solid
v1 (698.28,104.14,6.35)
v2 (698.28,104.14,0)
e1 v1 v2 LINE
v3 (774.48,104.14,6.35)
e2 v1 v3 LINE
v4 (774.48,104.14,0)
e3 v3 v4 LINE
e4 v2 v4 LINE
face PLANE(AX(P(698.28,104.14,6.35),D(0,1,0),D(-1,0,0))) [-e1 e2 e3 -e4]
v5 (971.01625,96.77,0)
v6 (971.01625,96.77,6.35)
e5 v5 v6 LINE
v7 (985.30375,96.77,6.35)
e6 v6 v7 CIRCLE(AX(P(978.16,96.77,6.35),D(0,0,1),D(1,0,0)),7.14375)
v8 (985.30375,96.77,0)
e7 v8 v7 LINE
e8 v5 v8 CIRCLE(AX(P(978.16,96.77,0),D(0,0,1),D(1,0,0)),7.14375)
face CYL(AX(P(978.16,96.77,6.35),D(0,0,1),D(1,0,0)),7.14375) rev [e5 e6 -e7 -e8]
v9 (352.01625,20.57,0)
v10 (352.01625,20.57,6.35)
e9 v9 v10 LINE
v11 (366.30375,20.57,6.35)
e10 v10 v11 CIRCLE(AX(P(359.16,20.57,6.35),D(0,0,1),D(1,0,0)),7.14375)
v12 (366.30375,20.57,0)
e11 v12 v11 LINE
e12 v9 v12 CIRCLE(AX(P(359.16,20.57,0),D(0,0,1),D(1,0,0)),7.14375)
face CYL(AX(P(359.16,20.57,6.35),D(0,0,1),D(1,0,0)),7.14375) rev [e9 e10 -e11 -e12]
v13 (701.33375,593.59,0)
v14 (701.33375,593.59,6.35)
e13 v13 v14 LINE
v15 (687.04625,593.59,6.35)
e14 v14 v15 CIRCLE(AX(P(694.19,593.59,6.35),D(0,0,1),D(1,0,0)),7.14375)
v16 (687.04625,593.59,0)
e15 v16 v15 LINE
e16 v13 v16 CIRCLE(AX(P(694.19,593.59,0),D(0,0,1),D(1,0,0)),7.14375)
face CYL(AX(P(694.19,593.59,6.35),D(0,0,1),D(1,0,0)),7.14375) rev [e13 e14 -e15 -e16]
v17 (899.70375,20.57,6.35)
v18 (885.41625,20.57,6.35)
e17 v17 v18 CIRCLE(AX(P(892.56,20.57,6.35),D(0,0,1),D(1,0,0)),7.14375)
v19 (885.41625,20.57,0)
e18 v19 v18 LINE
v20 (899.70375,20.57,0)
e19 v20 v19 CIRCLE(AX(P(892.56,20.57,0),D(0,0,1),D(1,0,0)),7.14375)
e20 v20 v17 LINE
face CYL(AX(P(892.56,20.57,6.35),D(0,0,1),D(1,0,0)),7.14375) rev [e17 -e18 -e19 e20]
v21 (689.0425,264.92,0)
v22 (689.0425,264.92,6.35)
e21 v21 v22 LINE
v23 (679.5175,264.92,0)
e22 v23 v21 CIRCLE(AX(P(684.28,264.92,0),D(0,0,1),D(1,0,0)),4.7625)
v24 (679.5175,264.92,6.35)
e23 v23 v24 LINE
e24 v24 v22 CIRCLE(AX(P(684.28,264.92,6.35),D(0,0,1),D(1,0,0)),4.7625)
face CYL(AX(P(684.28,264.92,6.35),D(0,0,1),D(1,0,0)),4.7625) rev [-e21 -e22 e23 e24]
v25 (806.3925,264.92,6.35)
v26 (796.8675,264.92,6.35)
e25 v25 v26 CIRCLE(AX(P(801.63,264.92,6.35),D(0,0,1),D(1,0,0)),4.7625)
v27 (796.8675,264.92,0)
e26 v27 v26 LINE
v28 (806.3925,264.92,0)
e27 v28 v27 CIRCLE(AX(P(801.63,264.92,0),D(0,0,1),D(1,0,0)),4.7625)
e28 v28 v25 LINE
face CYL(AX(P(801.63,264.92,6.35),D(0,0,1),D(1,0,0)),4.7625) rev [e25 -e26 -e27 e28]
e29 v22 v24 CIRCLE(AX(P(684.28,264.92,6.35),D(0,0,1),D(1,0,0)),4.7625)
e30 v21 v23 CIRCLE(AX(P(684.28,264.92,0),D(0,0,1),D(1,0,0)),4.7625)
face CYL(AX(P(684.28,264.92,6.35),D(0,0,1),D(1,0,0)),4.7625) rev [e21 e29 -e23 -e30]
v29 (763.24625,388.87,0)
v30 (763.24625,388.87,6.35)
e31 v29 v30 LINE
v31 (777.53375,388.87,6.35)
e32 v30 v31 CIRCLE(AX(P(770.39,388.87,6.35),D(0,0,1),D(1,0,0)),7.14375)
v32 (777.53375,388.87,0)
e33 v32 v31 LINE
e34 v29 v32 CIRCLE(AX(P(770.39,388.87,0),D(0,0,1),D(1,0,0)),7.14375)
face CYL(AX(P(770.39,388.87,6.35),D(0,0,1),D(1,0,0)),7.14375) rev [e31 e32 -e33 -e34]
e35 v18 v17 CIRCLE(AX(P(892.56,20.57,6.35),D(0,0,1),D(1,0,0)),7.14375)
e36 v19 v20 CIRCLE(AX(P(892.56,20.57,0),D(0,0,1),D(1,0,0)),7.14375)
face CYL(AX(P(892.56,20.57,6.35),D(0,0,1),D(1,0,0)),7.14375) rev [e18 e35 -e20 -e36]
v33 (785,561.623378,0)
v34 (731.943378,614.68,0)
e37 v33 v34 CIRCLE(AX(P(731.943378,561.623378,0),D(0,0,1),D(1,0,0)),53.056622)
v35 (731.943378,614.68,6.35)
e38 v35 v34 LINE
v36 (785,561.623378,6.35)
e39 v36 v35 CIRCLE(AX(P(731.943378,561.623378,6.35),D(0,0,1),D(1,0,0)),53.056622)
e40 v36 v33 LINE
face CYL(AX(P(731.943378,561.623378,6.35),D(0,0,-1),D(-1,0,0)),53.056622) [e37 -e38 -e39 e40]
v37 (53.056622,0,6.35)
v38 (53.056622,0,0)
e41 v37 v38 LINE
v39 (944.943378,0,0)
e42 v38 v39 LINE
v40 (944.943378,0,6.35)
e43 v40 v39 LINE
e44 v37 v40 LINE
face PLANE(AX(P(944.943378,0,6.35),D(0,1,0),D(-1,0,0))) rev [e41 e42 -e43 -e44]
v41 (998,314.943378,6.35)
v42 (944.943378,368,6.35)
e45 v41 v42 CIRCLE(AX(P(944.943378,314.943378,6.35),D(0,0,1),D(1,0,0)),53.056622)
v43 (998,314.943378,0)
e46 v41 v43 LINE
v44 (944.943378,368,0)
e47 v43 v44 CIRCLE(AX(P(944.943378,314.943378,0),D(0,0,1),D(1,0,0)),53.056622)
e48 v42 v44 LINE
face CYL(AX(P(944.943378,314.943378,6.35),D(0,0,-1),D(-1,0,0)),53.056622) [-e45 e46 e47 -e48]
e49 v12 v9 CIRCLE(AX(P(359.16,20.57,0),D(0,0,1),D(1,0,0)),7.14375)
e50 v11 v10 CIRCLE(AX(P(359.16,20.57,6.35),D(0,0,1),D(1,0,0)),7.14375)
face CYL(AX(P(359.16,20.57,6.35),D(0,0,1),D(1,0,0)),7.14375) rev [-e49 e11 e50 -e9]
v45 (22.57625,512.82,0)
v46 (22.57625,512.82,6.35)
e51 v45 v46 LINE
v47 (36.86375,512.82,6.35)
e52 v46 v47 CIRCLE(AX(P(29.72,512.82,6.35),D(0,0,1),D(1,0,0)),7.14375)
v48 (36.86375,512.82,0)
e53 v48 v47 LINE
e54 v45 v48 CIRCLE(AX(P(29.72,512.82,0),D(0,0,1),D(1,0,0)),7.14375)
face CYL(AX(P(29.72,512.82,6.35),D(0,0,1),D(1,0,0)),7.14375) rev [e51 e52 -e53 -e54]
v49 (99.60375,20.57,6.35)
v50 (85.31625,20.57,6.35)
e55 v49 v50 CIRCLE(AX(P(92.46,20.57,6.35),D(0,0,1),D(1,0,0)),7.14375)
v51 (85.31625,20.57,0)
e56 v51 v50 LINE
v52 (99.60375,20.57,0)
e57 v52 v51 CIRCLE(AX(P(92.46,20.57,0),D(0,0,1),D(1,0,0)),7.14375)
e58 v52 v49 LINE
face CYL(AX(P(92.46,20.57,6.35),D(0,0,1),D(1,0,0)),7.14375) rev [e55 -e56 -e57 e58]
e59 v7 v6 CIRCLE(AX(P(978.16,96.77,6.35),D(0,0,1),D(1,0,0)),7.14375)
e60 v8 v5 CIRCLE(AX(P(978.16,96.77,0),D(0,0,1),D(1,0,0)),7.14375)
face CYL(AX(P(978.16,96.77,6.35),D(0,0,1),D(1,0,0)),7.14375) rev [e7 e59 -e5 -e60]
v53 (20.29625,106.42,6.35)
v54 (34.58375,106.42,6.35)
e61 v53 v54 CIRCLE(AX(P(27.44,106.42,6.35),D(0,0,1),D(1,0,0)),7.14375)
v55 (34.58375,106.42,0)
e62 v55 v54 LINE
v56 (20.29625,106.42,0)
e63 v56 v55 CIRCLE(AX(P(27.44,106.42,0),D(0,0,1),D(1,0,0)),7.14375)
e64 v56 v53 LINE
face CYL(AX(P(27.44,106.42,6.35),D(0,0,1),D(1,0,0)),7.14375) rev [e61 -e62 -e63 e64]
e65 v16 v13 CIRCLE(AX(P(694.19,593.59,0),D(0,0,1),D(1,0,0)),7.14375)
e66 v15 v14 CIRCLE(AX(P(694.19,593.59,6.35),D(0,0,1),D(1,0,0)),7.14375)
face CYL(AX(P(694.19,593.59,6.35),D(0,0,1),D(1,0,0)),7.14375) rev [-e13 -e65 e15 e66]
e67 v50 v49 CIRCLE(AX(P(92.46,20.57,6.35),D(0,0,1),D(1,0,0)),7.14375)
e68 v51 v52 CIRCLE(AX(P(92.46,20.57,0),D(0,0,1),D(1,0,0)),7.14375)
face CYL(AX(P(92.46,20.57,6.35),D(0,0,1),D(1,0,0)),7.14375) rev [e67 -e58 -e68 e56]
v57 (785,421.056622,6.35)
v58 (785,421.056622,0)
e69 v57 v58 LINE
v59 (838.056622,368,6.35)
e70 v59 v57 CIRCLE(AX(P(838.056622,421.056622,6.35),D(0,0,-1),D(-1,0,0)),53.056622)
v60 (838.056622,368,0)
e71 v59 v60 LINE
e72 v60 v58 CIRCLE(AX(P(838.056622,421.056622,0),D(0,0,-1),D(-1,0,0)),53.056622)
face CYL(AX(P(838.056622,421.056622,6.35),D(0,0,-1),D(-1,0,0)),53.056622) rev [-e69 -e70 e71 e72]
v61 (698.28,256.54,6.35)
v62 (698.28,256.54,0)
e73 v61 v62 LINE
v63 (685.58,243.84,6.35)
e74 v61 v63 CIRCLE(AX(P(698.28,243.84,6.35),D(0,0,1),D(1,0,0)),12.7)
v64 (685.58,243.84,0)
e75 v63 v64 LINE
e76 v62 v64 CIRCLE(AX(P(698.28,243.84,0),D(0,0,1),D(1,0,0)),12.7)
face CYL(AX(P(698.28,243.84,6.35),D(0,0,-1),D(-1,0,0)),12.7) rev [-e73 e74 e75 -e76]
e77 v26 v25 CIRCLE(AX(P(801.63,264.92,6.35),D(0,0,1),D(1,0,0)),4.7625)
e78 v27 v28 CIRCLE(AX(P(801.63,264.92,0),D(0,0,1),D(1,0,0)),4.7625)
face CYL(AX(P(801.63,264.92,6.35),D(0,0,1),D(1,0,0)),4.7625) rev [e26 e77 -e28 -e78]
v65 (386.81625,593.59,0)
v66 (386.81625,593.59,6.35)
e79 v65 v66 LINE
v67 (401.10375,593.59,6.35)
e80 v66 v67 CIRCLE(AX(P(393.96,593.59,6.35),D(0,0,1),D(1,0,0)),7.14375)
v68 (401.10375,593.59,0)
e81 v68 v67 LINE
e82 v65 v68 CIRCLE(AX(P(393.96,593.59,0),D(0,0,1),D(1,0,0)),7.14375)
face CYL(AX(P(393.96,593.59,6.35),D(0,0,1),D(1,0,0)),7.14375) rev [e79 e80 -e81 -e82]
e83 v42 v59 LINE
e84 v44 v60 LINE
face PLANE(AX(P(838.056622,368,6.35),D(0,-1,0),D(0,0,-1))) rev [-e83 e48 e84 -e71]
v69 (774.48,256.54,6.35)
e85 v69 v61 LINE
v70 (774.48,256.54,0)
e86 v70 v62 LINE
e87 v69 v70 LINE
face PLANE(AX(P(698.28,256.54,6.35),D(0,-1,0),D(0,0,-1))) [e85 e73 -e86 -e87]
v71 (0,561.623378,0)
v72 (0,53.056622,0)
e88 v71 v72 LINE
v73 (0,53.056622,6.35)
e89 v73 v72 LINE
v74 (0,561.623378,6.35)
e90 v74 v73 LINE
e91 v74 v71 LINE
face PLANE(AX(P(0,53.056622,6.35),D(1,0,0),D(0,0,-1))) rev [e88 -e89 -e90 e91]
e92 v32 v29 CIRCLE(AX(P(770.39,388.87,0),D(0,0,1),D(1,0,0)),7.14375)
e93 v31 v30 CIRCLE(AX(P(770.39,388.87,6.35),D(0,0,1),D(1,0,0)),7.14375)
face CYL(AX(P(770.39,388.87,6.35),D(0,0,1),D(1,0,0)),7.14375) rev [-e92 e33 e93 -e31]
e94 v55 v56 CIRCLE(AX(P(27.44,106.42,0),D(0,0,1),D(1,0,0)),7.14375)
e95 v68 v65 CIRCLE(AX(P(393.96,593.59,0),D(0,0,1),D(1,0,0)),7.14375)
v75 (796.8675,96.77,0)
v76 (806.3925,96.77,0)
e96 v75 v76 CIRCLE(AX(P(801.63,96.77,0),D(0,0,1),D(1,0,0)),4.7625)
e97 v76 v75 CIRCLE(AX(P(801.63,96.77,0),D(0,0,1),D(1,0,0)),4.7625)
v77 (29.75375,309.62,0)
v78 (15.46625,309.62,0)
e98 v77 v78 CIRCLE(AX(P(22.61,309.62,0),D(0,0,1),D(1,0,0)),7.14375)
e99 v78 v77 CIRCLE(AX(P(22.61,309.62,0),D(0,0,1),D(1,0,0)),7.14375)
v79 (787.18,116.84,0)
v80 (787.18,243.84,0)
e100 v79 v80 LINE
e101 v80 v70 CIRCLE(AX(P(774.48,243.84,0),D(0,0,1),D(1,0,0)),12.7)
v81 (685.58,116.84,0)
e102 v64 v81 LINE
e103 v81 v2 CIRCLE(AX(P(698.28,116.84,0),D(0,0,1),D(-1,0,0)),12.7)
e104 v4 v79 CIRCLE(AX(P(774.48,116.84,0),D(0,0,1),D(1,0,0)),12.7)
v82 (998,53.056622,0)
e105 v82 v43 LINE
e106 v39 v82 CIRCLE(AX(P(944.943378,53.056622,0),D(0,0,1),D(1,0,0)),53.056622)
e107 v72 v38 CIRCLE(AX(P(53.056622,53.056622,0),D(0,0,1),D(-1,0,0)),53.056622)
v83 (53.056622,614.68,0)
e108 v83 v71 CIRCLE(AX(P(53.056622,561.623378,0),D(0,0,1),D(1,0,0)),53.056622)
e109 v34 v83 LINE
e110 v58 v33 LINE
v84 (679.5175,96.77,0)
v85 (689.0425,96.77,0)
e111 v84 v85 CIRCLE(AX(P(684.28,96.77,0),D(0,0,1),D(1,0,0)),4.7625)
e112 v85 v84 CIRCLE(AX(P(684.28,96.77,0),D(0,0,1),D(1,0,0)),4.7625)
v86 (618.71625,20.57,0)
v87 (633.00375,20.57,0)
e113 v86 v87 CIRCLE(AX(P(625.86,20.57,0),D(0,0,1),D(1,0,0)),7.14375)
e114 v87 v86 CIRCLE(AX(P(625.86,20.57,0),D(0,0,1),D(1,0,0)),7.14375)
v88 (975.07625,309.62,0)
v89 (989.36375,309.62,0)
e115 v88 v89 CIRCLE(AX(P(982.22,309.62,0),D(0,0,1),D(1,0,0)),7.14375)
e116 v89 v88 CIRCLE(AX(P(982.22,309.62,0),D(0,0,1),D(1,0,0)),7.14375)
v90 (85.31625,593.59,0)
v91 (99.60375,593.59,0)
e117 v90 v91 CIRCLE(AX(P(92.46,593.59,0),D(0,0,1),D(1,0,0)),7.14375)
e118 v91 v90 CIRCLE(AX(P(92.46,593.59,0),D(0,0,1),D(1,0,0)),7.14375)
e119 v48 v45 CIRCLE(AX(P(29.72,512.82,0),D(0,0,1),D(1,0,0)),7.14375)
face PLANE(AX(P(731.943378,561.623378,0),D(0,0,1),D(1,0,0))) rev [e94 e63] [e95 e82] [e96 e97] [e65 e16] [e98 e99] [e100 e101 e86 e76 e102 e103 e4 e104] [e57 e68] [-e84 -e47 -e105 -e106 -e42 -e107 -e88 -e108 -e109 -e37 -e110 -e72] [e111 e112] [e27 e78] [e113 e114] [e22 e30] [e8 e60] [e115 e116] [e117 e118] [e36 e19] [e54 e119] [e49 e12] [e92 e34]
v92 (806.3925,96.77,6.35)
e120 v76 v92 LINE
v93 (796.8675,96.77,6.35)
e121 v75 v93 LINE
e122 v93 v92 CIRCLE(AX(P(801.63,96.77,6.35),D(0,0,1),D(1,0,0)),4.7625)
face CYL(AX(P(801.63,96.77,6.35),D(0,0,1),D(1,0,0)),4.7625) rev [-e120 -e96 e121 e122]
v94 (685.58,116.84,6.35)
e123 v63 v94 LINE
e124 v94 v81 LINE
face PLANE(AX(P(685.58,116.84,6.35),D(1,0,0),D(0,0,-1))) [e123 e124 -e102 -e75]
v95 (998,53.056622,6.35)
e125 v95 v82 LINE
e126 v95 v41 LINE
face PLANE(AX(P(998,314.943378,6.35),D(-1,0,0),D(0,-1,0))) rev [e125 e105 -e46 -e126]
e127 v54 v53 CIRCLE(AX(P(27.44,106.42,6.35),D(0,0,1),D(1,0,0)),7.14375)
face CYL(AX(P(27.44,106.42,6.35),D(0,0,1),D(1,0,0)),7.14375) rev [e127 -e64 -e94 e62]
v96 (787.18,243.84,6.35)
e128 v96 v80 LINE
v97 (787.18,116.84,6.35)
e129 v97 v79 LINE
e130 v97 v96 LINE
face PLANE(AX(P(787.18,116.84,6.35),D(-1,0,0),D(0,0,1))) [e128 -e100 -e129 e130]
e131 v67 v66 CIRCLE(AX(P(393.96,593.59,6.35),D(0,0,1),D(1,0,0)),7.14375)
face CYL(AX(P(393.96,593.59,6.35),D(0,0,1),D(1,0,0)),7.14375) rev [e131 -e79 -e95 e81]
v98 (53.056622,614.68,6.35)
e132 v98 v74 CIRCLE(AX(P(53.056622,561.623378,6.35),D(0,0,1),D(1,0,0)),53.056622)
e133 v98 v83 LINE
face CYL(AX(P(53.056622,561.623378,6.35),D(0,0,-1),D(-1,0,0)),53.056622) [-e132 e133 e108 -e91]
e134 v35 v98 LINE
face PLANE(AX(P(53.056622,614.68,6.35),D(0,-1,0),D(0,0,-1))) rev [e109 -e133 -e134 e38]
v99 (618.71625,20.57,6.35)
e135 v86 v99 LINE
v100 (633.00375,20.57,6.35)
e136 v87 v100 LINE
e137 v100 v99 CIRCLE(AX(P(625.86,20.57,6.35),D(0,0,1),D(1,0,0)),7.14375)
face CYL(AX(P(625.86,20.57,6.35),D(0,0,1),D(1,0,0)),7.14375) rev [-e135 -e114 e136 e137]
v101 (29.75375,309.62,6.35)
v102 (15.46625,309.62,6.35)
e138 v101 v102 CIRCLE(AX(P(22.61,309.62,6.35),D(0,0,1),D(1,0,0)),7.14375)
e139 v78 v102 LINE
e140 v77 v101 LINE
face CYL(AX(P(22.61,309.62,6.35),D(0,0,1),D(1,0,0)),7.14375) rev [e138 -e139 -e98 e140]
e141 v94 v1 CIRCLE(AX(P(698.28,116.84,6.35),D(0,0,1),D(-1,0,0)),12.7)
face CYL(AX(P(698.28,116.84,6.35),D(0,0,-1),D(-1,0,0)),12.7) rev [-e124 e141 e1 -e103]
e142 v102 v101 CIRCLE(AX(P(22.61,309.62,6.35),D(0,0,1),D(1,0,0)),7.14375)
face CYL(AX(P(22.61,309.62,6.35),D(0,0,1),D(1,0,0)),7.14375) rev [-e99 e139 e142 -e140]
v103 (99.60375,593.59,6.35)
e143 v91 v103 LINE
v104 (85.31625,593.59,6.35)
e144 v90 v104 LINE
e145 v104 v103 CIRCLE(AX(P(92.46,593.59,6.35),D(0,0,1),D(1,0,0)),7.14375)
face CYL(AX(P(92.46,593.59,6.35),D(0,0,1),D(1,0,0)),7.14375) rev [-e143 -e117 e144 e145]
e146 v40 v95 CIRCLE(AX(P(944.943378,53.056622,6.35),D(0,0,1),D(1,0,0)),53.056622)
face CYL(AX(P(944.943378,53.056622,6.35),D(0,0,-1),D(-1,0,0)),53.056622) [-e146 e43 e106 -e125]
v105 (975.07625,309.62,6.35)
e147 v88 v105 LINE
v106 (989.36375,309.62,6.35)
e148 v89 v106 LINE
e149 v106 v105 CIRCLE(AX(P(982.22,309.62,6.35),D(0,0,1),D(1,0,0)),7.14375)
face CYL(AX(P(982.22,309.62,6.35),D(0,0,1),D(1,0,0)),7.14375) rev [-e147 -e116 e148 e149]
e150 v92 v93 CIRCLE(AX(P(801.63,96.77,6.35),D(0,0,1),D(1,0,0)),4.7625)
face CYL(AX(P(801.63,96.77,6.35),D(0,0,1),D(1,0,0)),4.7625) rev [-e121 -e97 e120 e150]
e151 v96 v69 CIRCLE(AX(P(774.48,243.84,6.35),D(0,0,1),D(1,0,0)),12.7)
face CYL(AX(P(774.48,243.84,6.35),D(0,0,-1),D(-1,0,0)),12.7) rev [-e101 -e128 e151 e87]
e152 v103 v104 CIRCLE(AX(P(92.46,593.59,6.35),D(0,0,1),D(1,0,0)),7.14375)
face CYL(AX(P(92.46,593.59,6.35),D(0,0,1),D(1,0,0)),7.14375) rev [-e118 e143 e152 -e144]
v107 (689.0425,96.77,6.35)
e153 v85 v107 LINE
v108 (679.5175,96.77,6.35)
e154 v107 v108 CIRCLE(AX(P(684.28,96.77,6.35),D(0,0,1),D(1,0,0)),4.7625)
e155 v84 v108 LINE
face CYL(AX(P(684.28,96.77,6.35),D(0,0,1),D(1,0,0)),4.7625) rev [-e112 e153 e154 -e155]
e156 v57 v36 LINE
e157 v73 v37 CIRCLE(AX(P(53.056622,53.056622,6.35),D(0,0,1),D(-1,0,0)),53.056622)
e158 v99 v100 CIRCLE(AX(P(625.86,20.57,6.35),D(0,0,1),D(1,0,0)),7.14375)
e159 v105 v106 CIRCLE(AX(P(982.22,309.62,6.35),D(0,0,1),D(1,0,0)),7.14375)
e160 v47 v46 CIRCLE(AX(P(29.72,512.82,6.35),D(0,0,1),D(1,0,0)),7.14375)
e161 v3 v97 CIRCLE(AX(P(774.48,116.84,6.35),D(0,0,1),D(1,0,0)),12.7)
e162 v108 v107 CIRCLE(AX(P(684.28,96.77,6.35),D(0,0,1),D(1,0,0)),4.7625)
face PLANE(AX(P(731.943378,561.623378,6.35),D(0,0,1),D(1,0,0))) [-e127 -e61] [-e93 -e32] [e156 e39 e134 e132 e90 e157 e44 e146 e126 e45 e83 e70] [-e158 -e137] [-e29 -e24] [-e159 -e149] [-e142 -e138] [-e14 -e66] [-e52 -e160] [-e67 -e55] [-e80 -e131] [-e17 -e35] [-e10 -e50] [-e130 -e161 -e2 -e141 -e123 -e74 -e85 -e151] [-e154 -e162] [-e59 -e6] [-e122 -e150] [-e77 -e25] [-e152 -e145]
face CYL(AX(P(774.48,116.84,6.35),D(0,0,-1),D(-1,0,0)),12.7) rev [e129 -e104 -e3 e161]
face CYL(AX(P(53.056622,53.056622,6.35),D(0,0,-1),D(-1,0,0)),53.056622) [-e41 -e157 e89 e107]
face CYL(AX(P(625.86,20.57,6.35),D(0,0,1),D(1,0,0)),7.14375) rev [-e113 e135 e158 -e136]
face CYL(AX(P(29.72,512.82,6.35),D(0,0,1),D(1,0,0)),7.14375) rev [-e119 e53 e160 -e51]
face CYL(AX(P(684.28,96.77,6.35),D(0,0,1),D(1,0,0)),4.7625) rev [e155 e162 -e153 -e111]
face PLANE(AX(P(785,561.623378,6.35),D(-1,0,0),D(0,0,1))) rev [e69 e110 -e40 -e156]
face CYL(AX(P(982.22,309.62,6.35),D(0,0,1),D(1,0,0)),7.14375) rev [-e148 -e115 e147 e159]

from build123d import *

# Parameters (mm, degrees)
EXTRUDE1_DEPTH                 = 6.35
F_9_16_0_5625_DIAMETER_HOLE1_D = 14.2875
F_3_8_0_375_DIAMETER_HOLE1_D   = 9.525


with BuildPart() as part:
    # Sketch1 → Extrude1 (new body)
    with BuildSketch(Plane.XY):
        with BuildLine():
            Line((0, 53.05662155), (0, 561.62337845))
            ThreePointArc((0, 561.62337845), (15.539924665, 599.140075335), (53.05662155, 614.68))
            Line((53.05662155, 614.68), (731.94337845, 614.68))
            ThreePointArc((731.94337845, 614.68), (769.460075335, 599.140075335), (785, 561.62337845))
            Line((785, 561.62337845), (785, 421.05662155))
            ThreePointArc((785, 421.05662155), (800.539924665, 383.539924665), (838.05662155, 368))
            Line((838.05662155, 368), (944.94337845, 368))
            ThreePointArc((944.94337845, 368), (982.460075335, 352.460075335), (998, 314.94337845))
            Line((998, 314.94337845), (998, 53.05662155))
            ThreePointArc((998, 53.05662155), (982.460075335, 15.539924665), (944.94337845, 0))
            Line((944.94337845, 0), (53.05662155, 0))
            ThreePointArc((53.05662155, 0), (15.539924665, 15.539924665), (0, 53.05662155))
        make_face()
        with BuildLine():
            Line((698.28, 104.14), (774.48, 104.14))
            ThreePointArc((774.48, 104.14), (783.460256121, 107.859743879), (787.18, 116.84))
            Line((787.18, 116.84), (787.18, 243.84))
            ThreePointArc((787.18, 243.84), (783.460256121, 252.820256121), (774.48, 256.54))
            Line((774.48, 256.54), (698.28, 256.54))
            ThreePointArc((698.28, 256.54), (689.299743879, 252.820256121), (685.58, 243.84))
            Line((685.58, 243.84), (685.58, 116.84))
            ThreePointArc((685.58, 116.84), (689.299743879, 107.859743879), (698.28, 104.14))
        make_face(mode=Mode.SUBTRACT)
    extrude(amount=EXTRUDE1_DEPTH)

    # 9/16 (0.5625) Diameter Hole1 (through all)
    with Locations(Plane.XY.offset(6.35)):
        with Locations((22.61, 309.62), (29.72, 512.82), (27.44, 106.42), (92.46, 20.57), (92.46, 593.59), (694.19, 593.59), (393.96, 593.59), (359.16, 20.57), (625.86, 20.57), (892.56, 20.57), (978.16, 96.77), (982.22, 309.62), (770.39, 388.87)):
            Hole(F_9_16_0_5625_DIAMETER_HOLE1_D / 2)

    # 3/8 (0.375) Diameter Hole1 (through all)
    with Locations(Plane.XY.offset(6.35)):
        with Locations((684.28, 264.92), (684.28, 96.77), (801.63, 96.77), (801.63, 264.92)):
            Hole(F_3_8_0_375_DIAMETER_HOLE1_D / 2)


solid = part.part
